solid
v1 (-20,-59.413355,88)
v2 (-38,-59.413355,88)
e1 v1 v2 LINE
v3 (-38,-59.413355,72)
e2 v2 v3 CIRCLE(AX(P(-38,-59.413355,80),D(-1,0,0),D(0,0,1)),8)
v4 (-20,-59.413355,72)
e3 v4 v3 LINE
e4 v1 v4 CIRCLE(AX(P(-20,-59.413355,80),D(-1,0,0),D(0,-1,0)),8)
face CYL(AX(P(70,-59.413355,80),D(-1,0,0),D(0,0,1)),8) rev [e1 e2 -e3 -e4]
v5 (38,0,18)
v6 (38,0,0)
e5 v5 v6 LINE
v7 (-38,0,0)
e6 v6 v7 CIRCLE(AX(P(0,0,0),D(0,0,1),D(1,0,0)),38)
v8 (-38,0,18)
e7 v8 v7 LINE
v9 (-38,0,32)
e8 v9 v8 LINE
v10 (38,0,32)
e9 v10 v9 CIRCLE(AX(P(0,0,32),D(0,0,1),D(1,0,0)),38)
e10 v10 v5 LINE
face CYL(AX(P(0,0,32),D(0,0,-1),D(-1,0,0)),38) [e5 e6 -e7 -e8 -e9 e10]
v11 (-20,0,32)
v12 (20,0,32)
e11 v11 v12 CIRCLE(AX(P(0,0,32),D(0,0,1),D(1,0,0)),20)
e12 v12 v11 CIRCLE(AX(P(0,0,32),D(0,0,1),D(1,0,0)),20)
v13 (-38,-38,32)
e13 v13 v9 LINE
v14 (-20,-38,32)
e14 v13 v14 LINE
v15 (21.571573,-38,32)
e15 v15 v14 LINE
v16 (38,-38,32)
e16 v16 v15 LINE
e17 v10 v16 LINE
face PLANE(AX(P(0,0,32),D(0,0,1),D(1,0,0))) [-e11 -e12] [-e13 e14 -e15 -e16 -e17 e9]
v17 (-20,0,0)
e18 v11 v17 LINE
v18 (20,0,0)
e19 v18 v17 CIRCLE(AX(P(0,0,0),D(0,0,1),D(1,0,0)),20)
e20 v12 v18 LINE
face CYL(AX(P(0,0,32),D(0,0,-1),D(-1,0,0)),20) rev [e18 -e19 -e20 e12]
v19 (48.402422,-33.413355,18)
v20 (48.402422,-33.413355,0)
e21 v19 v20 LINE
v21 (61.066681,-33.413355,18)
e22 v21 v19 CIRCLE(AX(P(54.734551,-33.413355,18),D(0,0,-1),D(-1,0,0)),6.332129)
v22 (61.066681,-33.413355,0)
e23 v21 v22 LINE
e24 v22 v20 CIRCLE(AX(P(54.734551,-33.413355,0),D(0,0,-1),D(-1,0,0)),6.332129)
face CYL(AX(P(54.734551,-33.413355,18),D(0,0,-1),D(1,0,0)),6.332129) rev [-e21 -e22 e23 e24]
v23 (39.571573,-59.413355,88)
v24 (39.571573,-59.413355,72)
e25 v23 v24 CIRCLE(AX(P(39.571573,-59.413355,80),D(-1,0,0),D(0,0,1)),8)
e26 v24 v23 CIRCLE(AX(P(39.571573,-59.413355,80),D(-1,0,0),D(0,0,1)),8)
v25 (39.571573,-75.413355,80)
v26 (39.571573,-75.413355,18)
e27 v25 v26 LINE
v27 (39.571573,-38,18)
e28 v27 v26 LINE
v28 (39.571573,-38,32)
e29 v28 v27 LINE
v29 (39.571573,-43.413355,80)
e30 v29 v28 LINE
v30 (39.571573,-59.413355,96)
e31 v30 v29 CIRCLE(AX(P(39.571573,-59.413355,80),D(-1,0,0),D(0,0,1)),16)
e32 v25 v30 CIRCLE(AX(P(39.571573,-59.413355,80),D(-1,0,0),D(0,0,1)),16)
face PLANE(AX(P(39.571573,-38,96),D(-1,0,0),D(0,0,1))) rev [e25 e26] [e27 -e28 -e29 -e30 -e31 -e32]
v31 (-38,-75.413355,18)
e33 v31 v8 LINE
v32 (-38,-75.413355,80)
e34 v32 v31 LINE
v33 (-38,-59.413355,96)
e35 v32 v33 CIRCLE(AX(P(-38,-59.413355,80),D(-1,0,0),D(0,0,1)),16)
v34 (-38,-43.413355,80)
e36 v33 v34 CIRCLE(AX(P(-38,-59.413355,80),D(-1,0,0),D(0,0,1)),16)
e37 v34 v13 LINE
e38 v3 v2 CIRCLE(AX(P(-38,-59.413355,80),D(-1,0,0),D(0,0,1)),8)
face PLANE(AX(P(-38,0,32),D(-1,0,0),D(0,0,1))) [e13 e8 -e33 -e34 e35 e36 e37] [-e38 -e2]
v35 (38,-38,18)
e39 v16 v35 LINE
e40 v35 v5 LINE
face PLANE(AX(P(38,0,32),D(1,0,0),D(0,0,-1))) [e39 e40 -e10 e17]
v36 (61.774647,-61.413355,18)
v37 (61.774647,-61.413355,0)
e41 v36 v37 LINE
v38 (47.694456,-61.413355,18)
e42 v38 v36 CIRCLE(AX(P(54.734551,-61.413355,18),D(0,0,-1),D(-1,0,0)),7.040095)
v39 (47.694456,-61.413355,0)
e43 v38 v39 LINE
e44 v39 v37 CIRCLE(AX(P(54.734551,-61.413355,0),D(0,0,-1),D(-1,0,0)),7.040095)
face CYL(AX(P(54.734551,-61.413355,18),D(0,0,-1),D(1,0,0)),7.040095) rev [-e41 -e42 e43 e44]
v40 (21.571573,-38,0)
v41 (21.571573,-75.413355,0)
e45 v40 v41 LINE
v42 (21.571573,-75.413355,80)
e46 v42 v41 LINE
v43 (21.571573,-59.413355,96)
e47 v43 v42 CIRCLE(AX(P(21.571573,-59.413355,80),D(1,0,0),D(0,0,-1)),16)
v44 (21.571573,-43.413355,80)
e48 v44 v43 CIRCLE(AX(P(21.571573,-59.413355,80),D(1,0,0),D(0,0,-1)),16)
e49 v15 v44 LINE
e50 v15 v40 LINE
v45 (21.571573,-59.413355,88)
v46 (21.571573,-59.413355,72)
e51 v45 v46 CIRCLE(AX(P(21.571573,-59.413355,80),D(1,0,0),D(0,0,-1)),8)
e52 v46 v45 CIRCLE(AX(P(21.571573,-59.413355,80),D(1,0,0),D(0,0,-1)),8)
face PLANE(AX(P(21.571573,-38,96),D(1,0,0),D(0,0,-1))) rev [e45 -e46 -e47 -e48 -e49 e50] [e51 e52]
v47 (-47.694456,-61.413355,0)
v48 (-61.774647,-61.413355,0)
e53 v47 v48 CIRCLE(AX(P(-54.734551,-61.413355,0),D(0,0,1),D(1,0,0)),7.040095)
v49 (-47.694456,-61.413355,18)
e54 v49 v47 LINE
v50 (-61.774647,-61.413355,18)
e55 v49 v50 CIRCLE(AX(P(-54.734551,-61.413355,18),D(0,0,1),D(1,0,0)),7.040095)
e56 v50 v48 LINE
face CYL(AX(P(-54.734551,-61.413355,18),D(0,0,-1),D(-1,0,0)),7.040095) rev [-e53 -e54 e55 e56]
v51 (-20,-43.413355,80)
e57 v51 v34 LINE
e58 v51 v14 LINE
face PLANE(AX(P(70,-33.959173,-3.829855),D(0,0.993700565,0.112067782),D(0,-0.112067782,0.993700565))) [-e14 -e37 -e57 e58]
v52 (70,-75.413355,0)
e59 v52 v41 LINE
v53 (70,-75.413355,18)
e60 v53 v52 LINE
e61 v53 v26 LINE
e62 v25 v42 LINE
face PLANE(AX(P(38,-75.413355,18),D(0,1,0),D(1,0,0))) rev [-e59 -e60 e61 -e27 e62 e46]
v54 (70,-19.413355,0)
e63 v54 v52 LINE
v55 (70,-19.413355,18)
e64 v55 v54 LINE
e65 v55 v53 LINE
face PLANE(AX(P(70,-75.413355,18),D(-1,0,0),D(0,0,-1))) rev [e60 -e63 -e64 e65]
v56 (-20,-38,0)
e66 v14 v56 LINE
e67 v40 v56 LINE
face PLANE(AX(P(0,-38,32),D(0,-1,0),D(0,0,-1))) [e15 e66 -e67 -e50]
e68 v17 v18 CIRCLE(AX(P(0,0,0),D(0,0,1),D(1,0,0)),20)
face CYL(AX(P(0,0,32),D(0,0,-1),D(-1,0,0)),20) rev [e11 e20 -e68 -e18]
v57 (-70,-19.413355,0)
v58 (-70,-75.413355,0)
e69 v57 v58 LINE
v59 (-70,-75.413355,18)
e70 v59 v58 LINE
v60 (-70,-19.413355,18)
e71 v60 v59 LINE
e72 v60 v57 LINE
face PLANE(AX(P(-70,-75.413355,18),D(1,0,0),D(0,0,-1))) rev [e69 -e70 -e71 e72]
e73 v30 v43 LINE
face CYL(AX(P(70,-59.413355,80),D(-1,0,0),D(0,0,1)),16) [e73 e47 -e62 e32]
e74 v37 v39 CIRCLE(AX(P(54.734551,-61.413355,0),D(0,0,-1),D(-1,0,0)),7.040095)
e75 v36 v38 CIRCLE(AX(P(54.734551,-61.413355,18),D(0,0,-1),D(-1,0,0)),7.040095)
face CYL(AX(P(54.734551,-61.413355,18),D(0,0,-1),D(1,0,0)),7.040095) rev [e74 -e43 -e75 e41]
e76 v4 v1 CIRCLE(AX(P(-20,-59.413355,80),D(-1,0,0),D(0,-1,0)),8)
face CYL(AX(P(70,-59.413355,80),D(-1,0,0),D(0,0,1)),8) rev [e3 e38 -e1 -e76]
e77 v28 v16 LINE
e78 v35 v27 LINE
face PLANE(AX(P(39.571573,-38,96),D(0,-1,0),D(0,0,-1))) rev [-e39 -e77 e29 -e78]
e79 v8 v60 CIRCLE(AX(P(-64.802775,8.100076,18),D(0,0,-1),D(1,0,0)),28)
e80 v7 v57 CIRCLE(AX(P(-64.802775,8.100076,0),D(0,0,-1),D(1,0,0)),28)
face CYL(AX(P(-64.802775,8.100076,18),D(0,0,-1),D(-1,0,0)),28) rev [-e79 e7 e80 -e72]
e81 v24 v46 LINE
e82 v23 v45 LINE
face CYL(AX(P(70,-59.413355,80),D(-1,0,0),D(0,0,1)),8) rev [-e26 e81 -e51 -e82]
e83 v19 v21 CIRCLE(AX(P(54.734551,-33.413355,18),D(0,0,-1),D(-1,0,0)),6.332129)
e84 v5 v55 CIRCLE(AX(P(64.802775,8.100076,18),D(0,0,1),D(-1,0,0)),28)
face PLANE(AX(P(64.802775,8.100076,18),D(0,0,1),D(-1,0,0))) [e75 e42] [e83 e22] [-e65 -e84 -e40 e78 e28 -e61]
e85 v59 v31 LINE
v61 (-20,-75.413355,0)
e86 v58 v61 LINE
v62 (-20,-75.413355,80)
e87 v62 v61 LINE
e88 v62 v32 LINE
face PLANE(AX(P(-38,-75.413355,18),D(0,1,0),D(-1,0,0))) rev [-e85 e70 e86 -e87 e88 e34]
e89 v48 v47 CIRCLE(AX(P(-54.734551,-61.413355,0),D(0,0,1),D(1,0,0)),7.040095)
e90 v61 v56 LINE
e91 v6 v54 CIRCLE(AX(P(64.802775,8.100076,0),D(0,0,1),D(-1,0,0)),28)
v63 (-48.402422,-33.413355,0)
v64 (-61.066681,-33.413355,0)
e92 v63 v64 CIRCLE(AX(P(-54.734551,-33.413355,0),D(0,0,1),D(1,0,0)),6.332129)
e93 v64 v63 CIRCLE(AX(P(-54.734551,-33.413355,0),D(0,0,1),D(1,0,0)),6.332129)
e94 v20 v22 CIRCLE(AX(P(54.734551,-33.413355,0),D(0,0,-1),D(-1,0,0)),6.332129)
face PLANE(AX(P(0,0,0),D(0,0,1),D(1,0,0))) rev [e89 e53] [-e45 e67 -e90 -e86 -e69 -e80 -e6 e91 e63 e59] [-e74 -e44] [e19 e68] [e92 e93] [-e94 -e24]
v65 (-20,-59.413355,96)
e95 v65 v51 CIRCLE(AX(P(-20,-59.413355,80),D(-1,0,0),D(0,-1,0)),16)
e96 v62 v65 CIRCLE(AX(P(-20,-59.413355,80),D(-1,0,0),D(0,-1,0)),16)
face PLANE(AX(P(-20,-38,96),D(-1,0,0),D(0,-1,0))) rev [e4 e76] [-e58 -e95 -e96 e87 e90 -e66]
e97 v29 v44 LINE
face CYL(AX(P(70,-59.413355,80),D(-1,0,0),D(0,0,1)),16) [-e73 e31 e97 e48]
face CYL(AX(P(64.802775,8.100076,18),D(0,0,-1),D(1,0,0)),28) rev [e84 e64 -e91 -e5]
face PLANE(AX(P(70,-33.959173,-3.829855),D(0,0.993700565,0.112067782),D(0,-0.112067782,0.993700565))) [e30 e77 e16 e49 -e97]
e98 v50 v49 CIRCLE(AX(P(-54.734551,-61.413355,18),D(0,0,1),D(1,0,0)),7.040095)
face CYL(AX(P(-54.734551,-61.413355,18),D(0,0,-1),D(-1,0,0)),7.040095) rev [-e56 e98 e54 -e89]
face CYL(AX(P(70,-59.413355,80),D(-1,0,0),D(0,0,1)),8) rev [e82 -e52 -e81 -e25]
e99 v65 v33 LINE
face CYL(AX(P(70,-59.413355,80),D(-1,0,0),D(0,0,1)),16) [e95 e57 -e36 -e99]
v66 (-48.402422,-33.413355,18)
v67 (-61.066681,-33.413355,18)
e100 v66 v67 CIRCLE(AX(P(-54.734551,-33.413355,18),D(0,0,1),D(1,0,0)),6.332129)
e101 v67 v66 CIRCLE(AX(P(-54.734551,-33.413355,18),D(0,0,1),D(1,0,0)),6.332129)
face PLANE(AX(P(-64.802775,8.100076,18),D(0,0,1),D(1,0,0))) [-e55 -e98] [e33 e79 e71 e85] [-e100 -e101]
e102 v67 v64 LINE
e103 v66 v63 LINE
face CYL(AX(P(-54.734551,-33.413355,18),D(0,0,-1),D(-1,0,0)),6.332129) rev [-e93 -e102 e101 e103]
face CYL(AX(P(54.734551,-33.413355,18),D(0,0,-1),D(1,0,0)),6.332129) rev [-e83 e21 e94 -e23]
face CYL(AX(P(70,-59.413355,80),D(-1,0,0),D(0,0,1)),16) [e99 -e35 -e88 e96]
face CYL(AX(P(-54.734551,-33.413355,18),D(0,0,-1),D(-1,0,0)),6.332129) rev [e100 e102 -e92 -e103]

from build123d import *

# Parameters (mm, degrees)
HUB_BODY_PROFILE_R          = 20
HUB_BODY_DEPTH              = 32
MOUNTING_FLANGE_PROFILE_R   = 6.332129474
MOUNTING_FLANGE_PROFILE_R_2 = 7.040095354
MOUNTING_FLANGE_DEPTH       = 18
CLEVIS_ARMS_PROFILE_W       = 18
CLEVIS_ARMS_PROFILE_H       = 37.413354637
CLEVIS_ARMS_DEPTH           = 96
CLEVIS_SLOT_PROFILE_R       = 8
CLEVIS_SLOT_CUT_DEPTH       = 163.994398854


with BuildPart() as part:
    # Hub Body Profile → Hub Body (new body)
    with BuildSketch(Plane.XY):
        with BuildLine():
            Line((38, 0), (38, -38))
            Line((38, -38), (0, -38))
            Line((0, -38), (-38, -38))
            Line((-38, -38), (-38, 0))
            ThreePointArc((-38, 0), (0, 38), (38, 0))
        make_face()
        Circle(HUB_BODY_PROFILE_R, mode=Mode.SUBTRACT)
    extrude(amount=HUB_BODY_DEPTH)

    # Mounting Flange Profile → Mounting Flange (add)
    with BuildSketch(Plane.XY):
        with BuildLine():
            Line((-38, 0), (-38, -75.413354637))
            Line((-38, -75.413354637), (-70, -75.413354637))
            Line((-70, -75.413354637), (-70, -19.413354637))
            ThreePointArc((-70, -19.413354637), (-50.279706144, -15.839023099), (-38, 0))
        make_face()
        with Locations((-54.734551325, -33.413354637)):
            Circle(MOUNTING_FLANGE_PROFILE_R, mode=Mode.SUBTRACT)
        with Locations((-54.734551325, -61.413354637)):
            Circle(MOUNTING_FLANGE_PROFILE_R_2, mode=Mode.SUBTRACT)
    extrude(amount=MOUNTING_FLANGE_DEPTH)

    # Hub Body Mirror: part across plane


with BuildPart() as part_1:
    add(part.part)
    add(part.part.mirror(Plane(origin=(0, 0, 0), x_dir=(0, 0, 1), z_dir=(1, 0, 0))))

    # Clevis Arms Profile → Clevis Arms (add)
    with BuildSketch(Plane.XY):
        with Locations((-29, -56.706677318)):
            Rectangle(CLEVIS_ARMS_PROFILE_W, CLEVIS_ARMS_PROFILE_H)
        with Locations((30.571573125, -56.706677318)):
            Rectangle(CLEVIS_ARMS_PROFILE_W, CLEVIS_ARMS_PROFILE_H)
    extrude(amount=CLEVIS_ARMS_DEPTH)

    # Clevis Slot Profile → Clevis Slot Cut (cut, through all)
    with BuildSketch(Plane.ZY.offset(38)):
        with BuildLine():
            Line((32, -38), (80, -43.413354637))
            ThreePointArc((80, -43.413354637), (91.313708499, -48.099646138), (96, -59.413354637))
            Line((96, -59.413354637), (96, -38))
            Line((96, -38), (32, -38))
        make_face()
        with BuildLine():
            Line((96, -75.413354637), (96, -59.413354637))
            ThreePointArc((96, -59.413354637), (91.313708499, -70.727063136), (80, -75.413354637))
            Line((80, -75.413354637), (96, -75.413354637))
        make_face()
        with Locations((80, -59.413354637)):
            Circle(CLEVIS_SLOT_PROFILE_R)
    extrude(amount=-CLEVIS_SLOT_CUT_DEPTH, mode=Mode.SUBTRACT)


solid = part_1.part
